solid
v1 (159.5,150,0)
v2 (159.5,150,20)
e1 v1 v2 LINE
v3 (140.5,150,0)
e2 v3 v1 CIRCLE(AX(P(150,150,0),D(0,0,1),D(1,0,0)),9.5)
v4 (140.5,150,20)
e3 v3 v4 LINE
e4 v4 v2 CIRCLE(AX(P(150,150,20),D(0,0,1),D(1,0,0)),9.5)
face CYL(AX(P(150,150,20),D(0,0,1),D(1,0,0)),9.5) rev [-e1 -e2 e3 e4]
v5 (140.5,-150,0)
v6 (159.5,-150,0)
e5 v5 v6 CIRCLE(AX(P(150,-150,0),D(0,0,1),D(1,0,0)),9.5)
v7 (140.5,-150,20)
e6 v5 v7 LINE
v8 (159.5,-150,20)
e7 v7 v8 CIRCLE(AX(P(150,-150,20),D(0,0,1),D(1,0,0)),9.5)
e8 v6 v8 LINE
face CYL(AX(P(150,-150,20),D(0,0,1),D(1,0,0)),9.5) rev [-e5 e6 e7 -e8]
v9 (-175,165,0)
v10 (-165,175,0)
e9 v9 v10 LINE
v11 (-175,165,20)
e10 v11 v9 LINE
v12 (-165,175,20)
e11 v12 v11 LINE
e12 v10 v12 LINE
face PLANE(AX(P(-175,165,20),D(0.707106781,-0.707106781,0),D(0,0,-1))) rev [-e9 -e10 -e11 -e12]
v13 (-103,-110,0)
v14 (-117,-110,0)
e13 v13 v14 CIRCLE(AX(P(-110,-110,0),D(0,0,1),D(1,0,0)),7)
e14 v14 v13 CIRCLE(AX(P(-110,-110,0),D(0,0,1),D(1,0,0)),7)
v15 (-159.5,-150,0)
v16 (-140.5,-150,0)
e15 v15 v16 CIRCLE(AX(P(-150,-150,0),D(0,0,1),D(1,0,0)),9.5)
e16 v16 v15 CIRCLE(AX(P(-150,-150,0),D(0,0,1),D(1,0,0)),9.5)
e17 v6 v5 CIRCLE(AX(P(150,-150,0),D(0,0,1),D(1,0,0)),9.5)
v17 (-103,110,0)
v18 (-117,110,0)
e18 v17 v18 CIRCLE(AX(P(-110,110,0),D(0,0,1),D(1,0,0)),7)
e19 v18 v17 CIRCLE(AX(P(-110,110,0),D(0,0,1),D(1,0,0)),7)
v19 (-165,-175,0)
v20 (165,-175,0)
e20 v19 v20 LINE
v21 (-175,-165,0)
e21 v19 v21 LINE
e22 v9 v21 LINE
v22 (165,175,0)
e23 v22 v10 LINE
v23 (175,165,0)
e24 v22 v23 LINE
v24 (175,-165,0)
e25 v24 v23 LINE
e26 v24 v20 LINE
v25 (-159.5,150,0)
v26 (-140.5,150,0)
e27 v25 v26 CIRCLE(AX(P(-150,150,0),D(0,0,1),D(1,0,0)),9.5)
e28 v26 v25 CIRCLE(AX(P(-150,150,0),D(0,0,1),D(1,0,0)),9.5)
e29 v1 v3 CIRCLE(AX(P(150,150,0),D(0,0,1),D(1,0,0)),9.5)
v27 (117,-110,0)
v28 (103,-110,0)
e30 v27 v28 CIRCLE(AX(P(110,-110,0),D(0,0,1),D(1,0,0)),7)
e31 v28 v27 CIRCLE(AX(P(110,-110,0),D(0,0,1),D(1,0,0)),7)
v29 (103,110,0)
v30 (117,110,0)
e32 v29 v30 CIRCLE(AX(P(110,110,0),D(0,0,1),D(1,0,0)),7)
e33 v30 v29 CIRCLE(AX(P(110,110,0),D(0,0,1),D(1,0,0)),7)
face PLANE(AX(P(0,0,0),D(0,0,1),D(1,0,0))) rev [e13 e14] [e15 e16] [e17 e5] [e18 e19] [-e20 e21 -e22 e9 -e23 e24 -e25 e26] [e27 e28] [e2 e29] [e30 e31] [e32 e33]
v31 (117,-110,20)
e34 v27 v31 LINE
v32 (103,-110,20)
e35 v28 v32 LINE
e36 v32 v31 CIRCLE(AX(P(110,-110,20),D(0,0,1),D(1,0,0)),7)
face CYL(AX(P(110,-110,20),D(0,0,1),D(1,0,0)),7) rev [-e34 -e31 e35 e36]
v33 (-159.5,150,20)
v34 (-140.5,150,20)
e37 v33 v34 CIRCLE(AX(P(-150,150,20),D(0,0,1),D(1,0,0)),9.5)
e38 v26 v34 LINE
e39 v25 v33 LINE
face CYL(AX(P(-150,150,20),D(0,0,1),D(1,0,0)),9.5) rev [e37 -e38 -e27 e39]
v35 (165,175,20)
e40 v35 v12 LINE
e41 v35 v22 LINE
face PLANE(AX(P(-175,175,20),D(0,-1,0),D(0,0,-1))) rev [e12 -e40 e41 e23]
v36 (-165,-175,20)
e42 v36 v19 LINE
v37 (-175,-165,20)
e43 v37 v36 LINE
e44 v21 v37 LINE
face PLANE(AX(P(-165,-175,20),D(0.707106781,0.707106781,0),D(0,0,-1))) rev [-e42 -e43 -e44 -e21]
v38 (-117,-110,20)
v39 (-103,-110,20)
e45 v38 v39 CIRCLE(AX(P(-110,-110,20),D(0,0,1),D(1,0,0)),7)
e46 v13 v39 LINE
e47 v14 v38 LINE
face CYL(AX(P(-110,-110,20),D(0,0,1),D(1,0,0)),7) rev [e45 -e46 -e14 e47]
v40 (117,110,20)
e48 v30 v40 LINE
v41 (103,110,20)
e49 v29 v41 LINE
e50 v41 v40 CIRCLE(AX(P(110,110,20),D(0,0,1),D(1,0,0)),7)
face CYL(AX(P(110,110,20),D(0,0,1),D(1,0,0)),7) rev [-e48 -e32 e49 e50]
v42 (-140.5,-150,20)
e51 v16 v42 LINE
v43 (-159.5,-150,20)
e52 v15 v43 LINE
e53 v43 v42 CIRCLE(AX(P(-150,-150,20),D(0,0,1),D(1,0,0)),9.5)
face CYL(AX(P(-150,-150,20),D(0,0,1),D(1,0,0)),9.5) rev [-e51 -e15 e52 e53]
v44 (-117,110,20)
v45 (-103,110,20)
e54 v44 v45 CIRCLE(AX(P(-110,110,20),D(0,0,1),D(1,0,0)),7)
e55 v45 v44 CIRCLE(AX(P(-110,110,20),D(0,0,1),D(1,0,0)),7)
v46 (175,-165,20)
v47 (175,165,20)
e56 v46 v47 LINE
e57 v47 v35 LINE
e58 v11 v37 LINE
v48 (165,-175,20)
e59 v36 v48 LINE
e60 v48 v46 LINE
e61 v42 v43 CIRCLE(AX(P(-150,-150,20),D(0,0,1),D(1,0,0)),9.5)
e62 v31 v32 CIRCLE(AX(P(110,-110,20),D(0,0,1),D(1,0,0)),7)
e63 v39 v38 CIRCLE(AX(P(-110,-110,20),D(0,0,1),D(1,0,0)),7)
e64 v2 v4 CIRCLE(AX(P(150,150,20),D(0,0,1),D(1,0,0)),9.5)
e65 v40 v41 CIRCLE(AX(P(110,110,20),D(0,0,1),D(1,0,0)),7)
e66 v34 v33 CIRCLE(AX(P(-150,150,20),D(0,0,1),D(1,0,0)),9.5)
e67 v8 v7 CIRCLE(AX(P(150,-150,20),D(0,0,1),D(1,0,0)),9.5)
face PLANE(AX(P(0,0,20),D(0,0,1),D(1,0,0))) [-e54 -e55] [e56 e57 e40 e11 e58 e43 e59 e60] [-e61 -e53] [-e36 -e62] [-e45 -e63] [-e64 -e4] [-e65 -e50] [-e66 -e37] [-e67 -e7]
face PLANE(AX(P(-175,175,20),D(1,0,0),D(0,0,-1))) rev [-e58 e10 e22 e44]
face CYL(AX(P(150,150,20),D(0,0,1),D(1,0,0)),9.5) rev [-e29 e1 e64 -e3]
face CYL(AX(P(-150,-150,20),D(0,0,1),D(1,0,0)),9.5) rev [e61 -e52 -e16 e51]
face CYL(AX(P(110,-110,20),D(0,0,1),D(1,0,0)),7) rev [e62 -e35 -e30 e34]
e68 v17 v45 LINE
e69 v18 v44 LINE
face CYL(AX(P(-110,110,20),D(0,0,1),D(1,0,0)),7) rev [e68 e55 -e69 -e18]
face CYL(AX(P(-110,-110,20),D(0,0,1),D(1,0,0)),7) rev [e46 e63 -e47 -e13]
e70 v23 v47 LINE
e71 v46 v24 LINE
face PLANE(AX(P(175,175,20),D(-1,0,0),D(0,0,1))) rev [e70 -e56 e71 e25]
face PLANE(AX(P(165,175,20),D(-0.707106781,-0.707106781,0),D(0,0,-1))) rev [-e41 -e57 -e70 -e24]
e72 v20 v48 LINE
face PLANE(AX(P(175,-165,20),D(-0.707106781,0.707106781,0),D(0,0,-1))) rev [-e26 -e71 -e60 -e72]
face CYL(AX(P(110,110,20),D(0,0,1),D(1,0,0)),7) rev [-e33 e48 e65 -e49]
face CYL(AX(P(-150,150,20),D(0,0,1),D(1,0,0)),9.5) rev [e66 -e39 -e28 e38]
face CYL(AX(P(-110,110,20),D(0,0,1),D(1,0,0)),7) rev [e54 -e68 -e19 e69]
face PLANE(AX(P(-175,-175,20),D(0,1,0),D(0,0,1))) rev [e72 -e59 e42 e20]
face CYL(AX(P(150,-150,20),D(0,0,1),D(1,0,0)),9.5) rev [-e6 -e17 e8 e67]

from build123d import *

# Parameters (mm, degrees)
SKETCH_1_W                  = 350
SKETCH_1_H                  = 350
EXTRUDE_1_DEPTH             = 20
HOLE_WIZARD_M16_1_D         = 14
HOLE_WIZARD_M16_1_DEPTH     = 42
HOLE_WIZARD_M16_1_TIP       = 4.206024333
HOLE_WIZARD_19_0_19_1_D     = 19
HOLE_WIZARD_19_0_19_1_DEPTH = 25
HOLE_WIZARD_19_0_19_1_TIP   = 5.708175881
CHAMFER_1_SIZE              = 10


with BuildPart() as part:
    # 草图1 → 凸台-拉伸1 (new body)
    with BuildSketch(Plane.XY):
        Rectangle(SKETCH_1_W, SKETCH_1_H)
    extrude(amount=EXTRUDE_1_DEPTH)

    # M16 螺纹孔1
    with Locations(Plane.XY.offset(20)):
        with Locations((110, 110), (-110, -110), (-110, 110), (110, -110)):
            Hole(HOLE_WIZARD_M16_1_D / 2, depth=HOLE_WIZARD_M16_1_DEPTH)
            with Locations((0, 0, -(HOLE_WIZARD_M16_1_DEPTH + HOLE_WIZARD_M16_1_TIP / 2))):  # 118° drill point
                Cone(0, HOLE_WIZARD_M16_1_D / 2, HOLE_WIZARD_M16_1_TIP, mode=Mode.SUBTRACT)

    # Ø19.0 (19) 直径孔1
    with Locations(Plane.XY.offset(20)):
        with Locations((150, 150), (-150, -150), (-150, 150), (150, -150)):
            Hole(HOLE_WIZARD_19_0_19_1_D / 2, depth=HOLE_WIZARD_19_0_19_1_DEPTH)
            with Locations((0, 0, -(HOLE_WIZARD_19_0_19_1_DEPTH + HOLE_WIZARD_19_0_19_1_TIP / 2))):  # 118° drill point
                Cone(0, HOLE_WIZARD_19_0_19_1_D / 2, HOLE_WIZARD_19_0_19_1_TIP, mode=Mode.SUBTRACT)

    # 倒角1
    chamfer_1_edges = [part.edges().sort_by_distance(p)[0] for p in [
        (175, -175, 10),
        (-175, -175, 10),
        (-175, 175, 10),
        (175, 175, 10),
    ]]
    chamfer(chamfer_1_edges, length=CHAMFER_1_SIZE)


solid = part.part
